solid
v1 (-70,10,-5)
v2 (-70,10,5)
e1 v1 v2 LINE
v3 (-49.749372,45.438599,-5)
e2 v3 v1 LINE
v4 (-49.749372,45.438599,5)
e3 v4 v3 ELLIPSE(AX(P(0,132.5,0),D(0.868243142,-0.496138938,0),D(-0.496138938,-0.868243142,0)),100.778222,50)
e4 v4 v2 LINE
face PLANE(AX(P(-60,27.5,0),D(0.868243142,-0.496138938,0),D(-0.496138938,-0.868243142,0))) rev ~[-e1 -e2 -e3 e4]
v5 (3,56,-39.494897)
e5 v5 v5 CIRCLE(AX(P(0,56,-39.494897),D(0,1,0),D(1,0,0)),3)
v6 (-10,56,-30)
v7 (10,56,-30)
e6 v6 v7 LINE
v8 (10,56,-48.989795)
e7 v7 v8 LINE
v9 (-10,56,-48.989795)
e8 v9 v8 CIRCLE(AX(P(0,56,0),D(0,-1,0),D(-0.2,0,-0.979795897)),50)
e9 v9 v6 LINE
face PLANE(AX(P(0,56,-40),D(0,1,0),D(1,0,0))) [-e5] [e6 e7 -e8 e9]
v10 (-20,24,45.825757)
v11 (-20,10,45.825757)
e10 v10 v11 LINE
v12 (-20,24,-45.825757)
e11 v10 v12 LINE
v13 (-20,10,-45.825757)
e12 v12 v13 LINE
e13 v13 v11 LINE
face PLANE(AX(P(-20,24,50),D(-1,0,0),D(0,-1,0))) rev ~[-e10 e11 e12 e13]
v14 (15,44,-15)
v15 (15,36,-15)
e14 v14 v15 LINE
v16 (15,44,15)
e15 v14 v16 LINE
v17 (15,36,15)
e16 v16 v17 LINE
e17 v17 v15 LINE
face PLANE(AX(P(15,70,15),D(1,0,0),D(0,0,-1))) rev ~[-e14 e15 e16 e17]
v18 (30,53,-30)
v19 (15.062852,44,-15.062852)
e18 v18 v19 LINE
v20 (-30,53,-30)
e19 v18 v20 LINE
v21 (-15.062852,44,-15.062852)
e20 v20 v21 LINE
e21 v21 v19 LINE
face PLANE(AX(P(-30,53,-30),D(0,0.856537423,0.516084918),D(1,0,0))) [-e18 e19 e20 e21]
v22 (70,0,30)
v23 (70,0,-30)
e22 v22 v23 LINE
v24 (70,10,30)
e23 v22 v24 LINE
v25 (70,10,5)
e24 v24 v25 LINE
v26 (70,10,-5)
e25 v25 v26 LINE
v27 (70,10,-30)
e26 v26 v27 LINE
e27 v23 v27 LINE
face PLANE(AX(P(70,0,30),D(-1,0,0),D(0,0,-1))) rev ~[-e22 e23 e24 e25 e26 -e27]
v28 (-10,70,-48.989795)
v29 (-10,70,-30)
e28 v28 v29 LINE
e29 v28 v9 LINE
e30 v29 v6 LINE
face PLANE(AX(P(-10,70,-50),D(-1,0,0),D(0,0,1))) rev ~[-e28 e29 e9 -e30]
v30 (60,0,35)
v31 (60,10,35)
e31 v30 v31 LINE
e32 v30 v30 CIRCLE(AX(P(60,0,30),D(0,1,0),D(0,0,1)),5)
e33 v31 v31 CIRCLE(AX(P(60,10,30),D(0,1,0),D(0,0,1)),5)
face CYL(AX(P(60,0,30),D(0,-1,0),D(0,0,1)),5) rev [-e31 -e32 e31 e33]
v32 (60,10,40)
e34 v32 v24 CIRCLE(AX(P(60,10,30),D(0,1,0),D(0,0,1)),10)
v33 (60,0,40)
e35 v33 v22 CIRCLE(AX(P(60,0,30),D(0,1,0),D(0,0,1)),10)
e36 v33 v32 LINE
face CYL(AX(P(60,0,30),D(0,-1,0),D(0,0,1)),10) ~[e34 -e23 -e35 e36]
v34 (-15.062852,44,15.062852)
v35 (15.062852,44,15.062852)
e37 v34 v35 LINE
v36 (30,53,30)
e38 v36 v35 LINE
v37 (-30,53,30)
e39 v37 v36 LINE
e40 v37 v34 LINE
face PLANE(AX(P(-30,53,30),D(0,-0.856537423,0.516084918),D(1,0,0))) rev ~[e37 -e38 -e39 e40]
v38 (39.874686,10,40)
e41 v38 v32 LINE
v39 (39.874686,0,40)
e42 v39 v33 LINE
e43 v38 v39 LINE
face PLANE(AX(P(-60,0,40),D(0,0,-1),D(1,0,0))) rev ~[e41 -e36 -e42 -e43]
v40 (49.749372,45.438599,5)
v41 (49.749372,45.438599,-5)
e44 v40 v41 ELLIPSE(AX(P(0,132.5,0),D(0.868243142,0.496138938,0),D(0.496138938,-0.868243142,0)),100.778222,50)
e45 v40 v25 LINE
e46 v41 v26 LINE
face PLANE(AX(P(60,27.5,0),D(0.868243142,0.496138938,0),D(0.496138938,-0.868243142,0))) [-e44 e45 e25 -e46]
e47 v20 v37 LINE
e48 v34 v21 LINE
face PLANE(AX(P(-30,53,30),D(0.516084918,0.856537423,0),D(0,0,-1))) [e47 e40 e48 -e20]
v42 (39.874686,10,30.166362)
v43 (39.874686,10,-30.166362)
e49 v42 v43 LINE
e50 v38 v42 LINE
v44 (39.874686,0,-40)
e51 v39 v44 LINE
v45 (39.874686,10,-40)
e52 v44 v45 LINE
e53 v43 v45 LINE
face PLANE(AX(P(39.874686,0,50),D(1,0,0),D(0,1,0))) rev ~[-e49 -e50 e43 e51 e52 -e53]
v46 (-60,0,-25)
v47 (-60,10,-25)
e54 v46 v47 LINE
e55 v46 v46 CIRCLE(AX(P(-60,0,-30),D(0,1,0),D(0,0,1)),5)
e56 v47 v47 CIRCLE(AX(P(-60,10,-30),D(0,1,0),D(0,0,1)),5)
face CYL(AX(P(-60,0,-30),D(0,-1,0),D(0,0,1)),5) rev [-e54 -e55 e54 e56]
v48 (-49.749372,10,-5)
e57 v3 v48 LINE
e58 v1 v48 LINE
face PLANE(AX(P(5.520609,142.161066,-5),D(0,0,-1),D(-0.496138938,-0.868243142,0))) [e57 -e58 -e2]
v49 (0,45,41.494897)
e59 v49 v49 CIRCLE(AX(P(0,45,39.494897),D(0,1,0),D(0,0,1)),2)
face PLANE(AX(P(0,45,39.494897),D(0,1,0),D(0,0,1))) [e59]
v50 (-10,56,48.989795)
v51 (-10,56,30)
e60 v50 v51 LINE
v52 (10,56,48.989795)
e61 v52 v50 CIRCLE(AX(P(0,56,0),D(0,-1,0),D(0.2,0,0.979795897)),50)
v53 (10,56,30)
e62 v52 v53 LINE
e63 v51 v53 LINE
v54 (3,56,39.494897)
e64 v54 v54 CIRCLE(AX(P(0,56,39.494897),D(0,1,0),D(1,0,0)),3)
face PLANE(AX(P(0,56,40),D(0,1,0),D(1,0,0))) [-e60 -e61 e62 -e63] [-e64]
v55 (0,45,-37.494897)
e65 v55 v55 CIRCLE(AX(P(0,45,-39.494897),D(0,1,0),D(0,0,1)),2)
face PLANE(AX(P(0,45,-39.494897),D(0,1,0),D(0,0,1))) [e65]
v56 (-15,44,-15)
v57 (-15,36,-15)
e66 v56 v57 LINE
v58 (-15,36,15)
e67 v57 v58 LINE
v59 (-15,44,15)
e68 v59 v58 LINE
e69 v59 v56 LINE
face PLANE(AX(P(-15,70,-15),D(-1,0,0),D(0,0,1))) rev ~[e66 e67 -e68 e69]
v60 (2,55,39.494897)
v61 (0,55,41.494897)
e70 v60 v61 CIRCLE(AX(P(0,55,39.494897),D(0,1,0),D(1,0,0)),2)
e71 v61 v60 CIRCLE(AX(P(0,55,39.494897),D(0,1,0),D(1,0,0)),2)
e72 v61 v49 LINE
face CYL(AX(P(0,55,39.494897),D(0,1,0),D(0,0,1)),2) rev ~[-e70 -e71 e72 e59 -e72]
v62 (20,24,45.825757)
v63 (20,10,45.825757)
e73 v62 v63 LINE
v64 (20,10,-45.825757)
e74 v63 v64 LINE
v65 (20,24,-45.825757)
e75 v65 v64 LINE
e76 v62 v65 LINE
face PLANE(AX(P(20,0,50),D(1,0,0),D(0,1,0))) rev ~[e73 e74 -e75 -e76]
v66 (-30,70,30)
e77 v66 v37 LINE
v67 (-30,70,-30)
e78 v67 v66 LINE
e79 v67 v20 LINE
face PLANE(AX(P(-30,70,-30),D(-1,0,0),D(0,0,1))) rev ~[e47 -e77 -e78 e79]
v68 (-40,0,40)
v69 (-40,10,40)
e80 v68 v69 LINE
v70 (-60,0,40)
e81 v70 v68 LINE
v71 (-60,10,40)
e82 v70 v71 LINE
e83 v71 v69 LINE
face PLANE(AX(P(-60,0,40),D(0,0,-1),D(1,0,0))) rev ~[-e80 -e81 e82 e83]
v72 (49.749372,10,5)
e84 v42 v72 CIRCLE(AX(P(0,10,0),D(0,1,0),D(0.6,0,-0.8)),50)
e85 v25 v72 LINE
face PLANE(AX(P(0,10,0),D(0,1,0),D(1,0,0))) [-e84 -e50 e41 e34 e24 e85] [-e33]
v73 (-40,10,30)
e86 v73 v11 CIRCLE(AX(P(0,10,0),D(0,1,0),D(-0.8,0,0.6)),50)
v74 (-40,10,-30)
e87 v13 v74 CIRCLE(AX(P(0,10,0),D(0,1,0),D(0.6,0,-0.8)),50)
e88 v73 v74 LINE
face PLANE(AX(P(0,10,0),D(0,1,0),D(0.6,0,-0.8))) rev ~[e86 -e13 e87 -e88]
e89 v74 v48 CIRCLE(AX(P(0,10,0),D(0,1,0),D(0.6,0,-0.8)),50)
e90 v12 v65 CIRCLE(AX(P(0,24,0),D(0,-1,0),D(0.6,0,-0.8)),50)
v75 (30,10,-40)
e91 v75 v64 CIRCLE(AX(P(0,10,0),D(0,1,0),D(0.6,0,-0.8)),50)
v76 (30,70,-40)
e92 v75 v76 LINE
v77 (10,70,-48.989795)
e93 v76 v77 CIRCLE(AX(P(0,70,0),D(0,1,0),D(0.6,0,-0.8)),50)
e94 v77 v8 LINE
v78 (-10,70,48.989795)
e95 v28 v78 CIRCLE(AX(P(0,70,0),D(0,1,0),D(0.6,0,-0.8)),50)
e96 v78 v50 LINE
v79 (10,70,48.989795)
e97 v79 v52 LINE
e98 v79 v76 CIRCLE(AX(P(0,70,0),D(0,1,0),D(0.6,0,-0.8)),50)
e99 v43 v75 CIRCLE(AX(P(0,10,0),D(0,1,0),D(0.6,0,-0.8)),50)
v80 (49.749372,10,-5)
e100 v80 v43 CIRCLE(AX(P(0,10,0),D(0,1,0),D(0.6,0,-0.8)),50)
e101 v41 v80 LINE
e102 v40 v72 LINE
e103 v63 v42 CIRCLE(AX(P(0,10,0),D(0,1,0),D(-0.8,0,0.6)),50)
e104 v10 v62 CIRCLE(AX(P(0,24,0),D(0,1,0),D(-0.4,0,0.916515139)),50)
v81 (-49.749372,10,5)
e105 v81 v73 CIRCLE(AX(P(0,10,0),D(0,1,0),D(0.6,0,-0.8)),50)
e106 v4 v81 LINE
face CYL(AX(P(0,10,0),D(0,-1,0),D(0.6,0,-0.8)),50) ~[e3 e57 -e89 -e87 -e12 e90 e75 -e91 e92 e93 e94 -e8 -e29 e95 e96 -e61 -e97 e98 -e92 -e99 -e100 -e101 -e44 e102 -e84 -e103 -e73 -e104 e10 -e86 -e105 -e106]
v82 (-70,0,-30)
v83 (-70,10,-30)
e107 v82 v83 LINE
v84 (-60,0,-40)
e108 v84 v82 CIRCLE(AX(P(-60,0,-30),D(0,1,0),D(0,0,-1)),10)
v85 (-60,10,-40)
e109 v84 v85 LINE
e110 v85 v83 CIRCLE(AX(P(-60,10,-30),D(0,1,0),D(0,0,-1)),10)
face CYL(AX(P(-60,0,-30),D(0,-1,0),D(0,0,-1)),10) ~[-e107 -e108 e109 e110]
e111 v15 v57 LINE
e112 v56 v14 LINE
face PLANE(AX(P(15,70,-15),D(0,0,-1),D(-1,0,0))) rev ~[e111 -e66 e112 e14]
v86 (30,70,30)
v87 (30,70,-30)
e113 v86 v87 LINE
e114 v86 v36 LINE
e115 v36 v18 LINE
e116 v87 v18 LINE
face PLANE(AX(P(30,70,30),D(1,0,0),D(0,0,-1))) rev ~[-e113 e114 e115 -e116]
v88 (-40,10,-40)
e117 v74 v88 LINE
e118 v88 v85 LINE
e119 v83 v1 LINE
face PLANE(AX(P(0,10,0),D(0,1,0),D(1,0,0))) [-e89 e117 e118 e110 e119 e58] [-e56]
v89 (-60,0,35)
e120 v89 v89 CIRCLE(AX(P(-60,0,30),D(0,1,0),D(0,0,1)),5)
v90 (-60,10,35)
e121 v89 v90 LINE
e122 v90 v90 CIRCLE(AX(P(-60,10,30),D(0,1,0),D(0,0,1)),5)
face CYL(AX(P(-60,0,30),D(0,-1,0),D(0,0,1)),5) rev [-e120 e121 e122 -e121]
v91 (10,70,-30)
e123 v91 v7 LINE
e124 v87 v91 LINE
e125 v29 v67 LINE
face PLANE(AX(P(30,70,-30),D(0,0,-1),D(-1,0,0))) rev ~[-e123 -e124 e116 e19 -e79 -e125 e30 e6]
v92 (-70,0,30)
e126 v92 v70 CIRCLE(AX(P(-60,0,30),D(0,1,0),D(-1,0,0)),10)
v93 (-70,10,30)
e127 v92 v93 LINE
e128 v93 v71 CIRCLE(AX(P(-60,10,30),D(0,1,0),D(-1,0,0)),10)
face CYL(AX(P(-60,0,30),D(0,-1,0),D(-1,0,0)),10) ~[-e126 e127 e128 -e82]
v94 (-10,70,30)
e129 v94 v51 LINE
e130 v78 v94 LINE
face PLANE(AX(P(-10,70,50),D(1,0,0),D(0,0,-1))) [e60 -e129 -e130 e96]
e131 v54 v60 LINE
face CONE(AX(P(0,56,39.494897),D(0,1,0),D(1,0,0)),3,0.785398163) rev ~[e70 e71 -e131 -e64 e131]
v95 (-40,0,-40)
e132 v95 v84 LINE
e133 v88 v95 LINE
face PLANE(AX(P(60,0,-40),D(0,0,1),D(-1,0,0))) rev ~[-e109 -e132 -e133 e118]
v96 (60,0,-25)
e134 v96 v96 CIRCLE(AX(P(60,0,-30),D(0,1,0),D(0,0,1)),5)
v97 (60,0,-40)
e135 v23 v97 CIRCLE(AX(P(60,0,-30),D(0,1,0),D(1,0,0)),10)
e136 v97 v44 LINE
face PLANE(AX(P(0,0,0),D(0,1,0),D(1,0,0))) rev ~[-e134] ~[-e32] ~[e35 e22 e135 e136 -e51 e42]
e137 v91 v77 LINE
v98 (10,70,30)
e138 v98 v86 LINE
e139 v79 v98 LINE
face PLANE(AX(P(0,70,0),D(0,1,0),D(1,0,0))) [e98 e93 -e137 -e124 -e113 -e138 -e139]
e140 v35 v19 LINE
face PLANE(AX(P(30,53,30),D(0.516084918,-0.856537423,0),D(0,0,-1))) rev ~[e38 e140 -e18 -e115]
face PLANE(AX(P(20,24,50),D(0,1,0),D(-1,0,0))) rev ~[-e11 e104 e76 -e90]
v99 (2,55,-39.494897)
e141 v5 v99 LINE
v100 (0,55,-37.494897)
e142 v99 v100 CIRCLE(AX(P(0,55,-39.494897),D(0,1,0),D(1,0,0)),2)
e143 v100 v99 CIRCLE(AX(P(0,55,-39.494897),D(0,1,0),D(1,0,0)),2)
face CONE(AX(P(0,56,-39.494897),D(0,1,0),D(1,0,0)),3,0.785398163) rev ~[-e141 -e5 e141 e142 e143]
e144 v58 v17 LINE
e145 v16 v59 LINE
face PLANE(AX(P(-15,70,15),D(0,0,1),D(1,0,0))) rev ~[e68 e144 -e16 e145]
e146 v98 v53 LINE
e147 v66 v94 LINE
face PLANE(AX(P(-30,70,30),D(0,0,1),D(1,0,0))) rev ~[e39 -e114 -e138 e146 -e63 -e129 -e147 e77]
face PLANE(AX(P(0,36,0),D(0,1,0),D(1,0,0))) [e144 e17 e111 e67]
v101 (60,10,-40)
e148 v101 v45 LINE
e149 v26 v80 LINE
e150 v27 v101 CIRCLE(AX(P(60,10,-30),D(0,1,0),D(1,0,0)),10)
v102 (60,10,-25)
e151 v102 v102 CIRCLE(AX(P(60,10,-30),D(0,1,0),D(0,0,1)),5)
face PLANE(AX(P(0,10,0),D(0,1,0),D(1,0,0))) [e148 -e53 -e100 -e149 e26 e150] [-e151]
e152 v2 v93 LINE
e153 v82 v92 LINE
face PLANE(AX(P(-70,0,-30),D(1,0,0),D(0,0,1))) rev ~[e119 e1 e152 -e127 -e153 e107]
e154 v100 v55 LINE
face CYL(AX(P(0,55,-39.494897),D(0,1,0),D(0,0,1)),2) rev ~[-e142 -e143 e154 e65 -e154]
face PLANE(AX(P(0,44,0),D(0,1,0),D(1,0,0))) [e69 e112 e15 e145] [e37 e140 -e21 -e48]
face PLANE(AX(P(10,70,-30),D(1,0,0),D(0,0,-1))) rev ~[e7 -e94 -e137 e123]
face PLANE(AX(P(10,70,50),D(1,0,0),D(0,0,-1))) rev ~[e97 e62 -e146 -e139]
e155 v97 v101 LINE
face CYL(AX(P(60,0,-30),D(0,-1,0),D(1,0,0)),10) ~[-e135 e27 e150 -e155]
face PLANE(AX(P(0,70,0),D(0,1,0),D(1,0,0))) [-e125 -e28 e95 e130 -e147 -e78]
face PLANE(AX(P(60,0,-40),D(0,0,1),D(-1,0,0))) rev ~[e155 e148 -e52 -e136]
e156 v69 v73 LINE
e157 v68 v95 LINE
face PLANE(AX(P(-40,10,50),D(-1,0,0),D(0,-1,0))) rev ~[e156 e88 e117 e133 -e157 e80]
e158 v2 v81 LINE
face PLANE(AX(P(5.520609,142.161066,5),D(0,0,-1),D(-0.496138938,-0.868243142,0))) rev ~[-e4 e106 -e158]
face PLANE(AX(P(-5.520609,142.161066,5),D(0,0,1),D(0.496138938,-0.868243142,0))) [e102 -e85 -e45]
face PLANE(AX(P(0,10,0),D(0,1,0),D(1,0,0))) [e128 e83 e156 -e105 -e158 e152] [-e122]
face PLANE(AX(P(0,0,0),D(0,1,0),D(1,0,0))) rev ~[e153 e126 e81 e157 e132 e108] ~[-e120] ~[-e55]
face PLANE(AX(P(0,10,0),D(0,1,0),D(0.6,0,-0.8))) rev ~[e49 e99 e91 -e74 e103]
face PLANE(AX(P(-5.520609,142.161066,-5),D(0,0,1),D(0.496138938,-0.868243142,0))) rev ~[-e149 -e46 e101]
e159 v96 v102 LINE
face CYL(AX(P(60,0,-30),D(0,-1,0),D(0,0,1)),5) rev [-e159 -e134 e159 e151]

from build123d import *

# Parameters (mm, degrees)
BASE_PLATE_SKETCH_R              = 5
BASE_PLATE_DEPTH                 = 10
BODY_CYLINDER_SKETCH_R           = 50
CYLINDRICAL_BODY_100_DEPTH       = 60
SQUARE_POCKET_60X60_DEPTH        = 17
LOWER_POCKET_DEPTH               = 17
DRAFTED_BOSS_SKETCH_W            = 30
DRAFTED_BOSS_SKETCH_H            = 30
DRAFTED_BOSS_DEPTH               = 9
DRAFTED_BOSS_DRAFT               = -58.93
SLOT_A_DEPTH                     = 34
INNER_BOSS_SKETCH_W              = 60
INNER_BOSS_SKETCH_H              = 60
INNER_BOSS_DEPTH                 = 44
SLOT_B_DEPTH                     = 34
CHANNEL_CUT_DEPTH                = 17
DRAFTED_CHANNEL_SKETCH_W         = 60
DRAFTED_CHANNEL_SKETCH_H         = 60
DRAFTED_CHANNEL_CUT_DEPTH        = 9
DRAFTED_CHANNEL_CUT_DRAFT        = -58.93
STEP_POCKET_SKETCH_W             = 20
STEP_POCKET_SKETCH_H             = 20
STEP_POCKET_DEPTH                = 14
PAD_HOLE_CHAMFER_SKETCH_R        = 3
PAD_HOLE_CHAMFER_DEPTH           = 1
PAD_HOLE_CHAMFER_DRAFT           = -45
PAD_HOLE_CHAMFER_PROFILE_2_DEPTH = 1
PAD_HOLE_CHAMFER_PROFILE_2_DRAFT = -45
PAD_HOLE_SKETCH_R                = 2
PAD_HOLE_DEPTH                   = 10
LEFT_SUPPORT_RIB_REACH           = 112.905
LEFT_RIB_SKETCH_WALL_W           = 264.12201887
LEFT_RIB_SKETCH_WALL_H           = 10
RIGHT_SUPPORT_RIB_REACH          = 112.905
RIGHT_RIB_SKETCH_WALL_W          = 264.12201887
RIGHT_RIB_SKETCH_WALL_H          = 10
SIDE_CUT_A_DEPTH                 = 126
SIDE_CUT_B_DEPTH                 = 202


with BuildPart() as part:
    # Base Plate Sketch → Base Plate (new body)
    with BuildSketch(Plane(origin=(0, 0, 0), x_dir=(1, 0, 0), z_dir=(0, 1, 0))):
        with BuildLine():
            Line((-60, -40), (0, -40))
            Line((0, -40), (60, -40))
            ThreePointArc((60, -40), (67.071067812, -37.071067812), (70, -30))
            Line((70, -30), (70, 0))
            Line((70, 0), (70, 30))
            ThreePointArc((70, 30), (67.071067812, 37.071067812), (60, 40))
            Line((60, 40), (-60, 40))
            ThreePointArc((-60, 40), (-67.071067812, 37.071067812), (-70, 30))
            Line((-70, 30), (-70, -30))
            ThreePointArc((-70, -30), (-67.071067812, -37.071067812), (-60, -40))
        make_face()
        with Locations(Location((-60, -30, 0), (0, 0, 270))):
            Circle(BASE_PLATE_SKETCH_R, mode=Mode.SUBTRACT)
        with Locations(Location((60, -30, 0), (0, 0, 270))):
            Circle(BASE_PLATE_SKETCH_R, mode=Mode.SUBTRACT)
        with Locations(Location((-60, 30, 0), (0, 0, 270))):
            Circle(BASE_PLATE_SKETCH_R, mode=Mode.SUBTRACT)
        with Locations(Location((60, 30, 0), (0, 0, 270))):
            Circle(BASE_PLATE_SKETCH_R, mode=Mode.SUBTRACT)
    extrude(amount=BASE_PLATE_DEPTH)

    # Body Cylinder Sketch → Cylindrical Body Ø100 (add)
    with BuildSketch(Plane(origin=(0, 10, 0), x_dir=(1, 0, 0), z_dir=(0, 1, 0))):
        with Locations(Location((0, 0, 0), (0, 0, 53.130102354))):
            Circle(BODY_CYLINDER_SKETCH_R)
    extrude(amount=CYLINDRICAL_BODY_100_DEPTH)

    # Square Pocket Sketch → Square Pocket 60x60 (cut)
    with BuildSketch(Plane(origin=(0, 70, 0), x_dir=(1, 0, 0), z_dir=(0, 1, 0))):
        Polygon((30, 0), (30, 30), (-30, 30), (-30, -30), (30, -30), align=None)
    extrude(amount=-SQUARE_POCKET_60X60_DEPTH, mode=Mode.SUBTRACT)

    # Lower Pocket Sketch → Lower Pocket (cut)
    with BuildSketch(Plane(origin=(0, 53, 0), x_dir=(1, 0, 0), z_dir=(0, 1, 0))):
        Polygon((15, 0), (15, 15), (-15, 15), (-15, -15), (15, -15), align=None)
    extrude(amount=-LOWER_POCKET_DEPTH, mode=Mode.SUBTRACT)


with BuildPart() as body_2:
    # Drafted Boss Sketch → Drafted Boss (with draft: the straight prism first)
    with BuildSketch(Plane(origin=(0, 53, 0), x_dir=(1, 0, 0), z_dir=(0, 1, 0))):
        Rectangle(DRAFTED_BOSS_SKETCH_W, DRAFTED_BOSS_SKETCH_H)
    extrude(amount=DRAFTED_BOSS_DEPTH)
    # Drafted Boss: the draft: its side faces are tilted about the plane it starts from
    drafted_boss_sides = [body_2.faces().sort_by_distance(p)[0] for p in [
        (-15, 57.5, 0),
        (0, 57.5, 15),
        (15, 57.5, 0),
        (0, 57.5, -15),
    ]]
    draft(drafted_boss_sides, Plane(origin=(0, 53, 0), x_dir=(1, 0, 0), z_dir=(0, 1, 0)), DRAFTED_BOSS_DRAFT)


with BuildPart() as slot_a_tool:
    # Slot A Sketch → Slot A (new body)
    with BuildSketch(Plane(origin=(0, 62, 0), x_dir=(1, 0, 0), z_dir=(0, 1, 0))):
        Polygon((15, 0), (15, 15), (-15, 15), (-15, -15), (15, -15), align=None)
    extrude(amount=-SLOT_A_DEPTH)


with BuildPart() as part_1:
    add(part.part)

    # Slot A: cut by slot_a_tool
    add(slot_a_tool.part, mode=Mode.SUBTRACT)



with BuildPart() as body_2_1:
    add(body_2.part)

    # Slot A: cut by slot_a_tool
    add(slot_a_tool.part, mode=Mode.SUBTRACT)


with BuildPart() as part_2:
    add(part_1.part)

    add(body_2_1.part)  # Inner Boss merges body 2
    # Inner Boss Sketch → Inner Boss (add)
    with BuildSketch(Plane(origin=(0, 70, 0), x_dir=(1, 0, 0), z_dir=(0, 1, 0))):
        Rectangle(INNER_BOSS_SKETCH_W, INNER_BOSS_SKETCH_H)
    extrude(amount=-INNER_BOSS_DEPTH)

    # Slot B Sketch → Slot B (cut)
    with BuildSketch(Plane(origin=(0, 70, 0), x_dir=(1, 0, 0), z_dir=(0, 1, 0))):
        Polygon((15, 0), (15, 15), (-15, 15), (-15, -15), (15, -15), align=None)
    extrude(amount=-SLOT_B_DEPTH, mode=Mode.SUBTRACT)

    # Channel Sketch → Channel Cut (cut)
    with BuildSketch(Plane(origin=(0, 70, 0), x_dir=(1, 0, 0), z_dir=(0, 1, 0))):
        Polygon((30, 0), (30, 30), (-30, 30), (-30, -30), (30, -30), align=None)
    extrude(amount=-CHANNEL_CUT_DEPTH, mode=Mode.SUBTRACT)


with BuildPart() as drafted_channel_cut_tool:
    # Drafted Channel Sketch → Drafted Channel Cut (with draft: the straight prism first)
    with BuildSketch(Plane(origin=(0, 53, 0), x_dir=(1, 0, 0), z_dir=(0, 1, 0))):
        Rectangle(DRAFTED_CHANNEL_SKETCH_W, DRAFTED_CHANNEL_SKETCH_H)
    extrude(amount=-DRAFTED_CHANNEL_CUT_DEPTH)
    # Drafted Channel Cut: the draft: its side faces are tilted about the plane it starts from
    drafted_channel_cut_sides = [drafted_channel_cut_tool.faces().sort_by_distance(p)[0] for p in [
        (-30, 48.5, 0),
        (0, 48.5, 30),
        (30, 48.5, 0),
        (0, 48.5, -30),
    ]]
    draft(drafted_channel_cut_sides, Plane(origin=(0, 53, 0), x_dir=(1, 0, 0), z_dir=(0, 1, 0)), DRAFTED_CHANNEL_CUT_DRAFT)


with BuildPart() as part_3:
    add(part_2.part)

    # Drafted Channel Cut: cut by drafted_channel_cut_tool
    add(drafted_channel_cut_tool.part, mode=Mode.SUBTRACT)

    # Step Pocket Sketch → Step Pocket (cut)
    with BuildSketch(Plane(origin=(0, 70, 0), x_dir=(1, 0, 0), z_dir=(0, 1, 0))):
        with Locations((0, -40)):
            Rectangle(STEP_POCKET_SKETCH_W, STEP_POCKET_SKETCH_H)
        Polygon((0, 30), (10, 30), (10, 50), (-10, 50), (-10, 30), align=None)
    extrude(amount=-STEP_POCKET_DEPTH, mode=Mode.SUBTRACT)


with BuildPart() as pad_hole_chamfer_tool:
    # Pad Hole Chamfer Sketch → Pad Hole Chamfer (with draft: the straight prism first)
    with BuildSketch(Plane(origin=(0, 56, 0), x_dir=(1, 0, 0), z_dir=(0, 1, 0))):
        with Locations((0, -39.494897428)):
            Circle(PAD_HOLE_CHAMFER_SKETCH_R)
    extrude(amount=-PAD_HOLE_CHAMFER_DEPTH)
    # Pad Hole Chamfer: the draft: its side faces are tilted about the plane it starts from
    pad_hole_chamfer_sides = [pad_hole_chamfer_tool.faces().sort_by_distance(p)[0] for p in [
        (-3, 55.5, 39.494897428),
    ]]
    draft(pad_hole_chamfer_sides, Plane(origin=(0, 56, 0), x_dir=(1, 0, 0), z_dir=(0, 1, 0)), PAD_HOLE_CHAMFER_DRAFT)


with BuildPart() as part_4:
    add(part_3.part)

    # Pad Hole Chamfer: cut by pad_hole_chamfer_tool
    add(pad_hole_chamfer_tool.part, mode=Mode.SUBTRACT)


with BuildPart() as pad_hole_chamfer_profile_2_tool:
    # Pad Hole Chamfer Sketch → Pad Hole Chamfer profile 2 (with draft: the straight prism first)
    with BuildSketch(Plane(origin=(0, 56, 0), x_dir=(1, 0, 0), z_dir=(0, 1, 0))):
        with Locations((0, 39.494897428)):
            Circle(PAD_HOLE_CHAMFER_SKETCH_R)
    extrude(amount=-PAD_HOLE_CHAMFER_PROFILE_2_DEPTH)
    # Pad Hole Chamfer profile 2: the draft: its side faces are tilted about the plane it starts from
    pad_hole_chamfer_profile_2_sides = [pad_hole_chamfer_profile_2_tool.faces().sort_by_distance(p)[0] for p in [
        (-3, 55.5, -39.494897428),
    ]]
    draft(pad_hole_chamfer_profile_2_sides, Plane(origin=(0, 56, 0), x_dir=(1, 0, 0), z_dir=(0, 1, 0)), PAD_HOLE_CHAMFER_PROFILE_2_DRAFT)


with BuildPart() as part_5:
    add(part_4.part)

    # Pad Hole Chamfer profile 2: cut by pad_hole_chamfer_profile_2_tool
    add(pad_hole_chamfer_profile_2_tool.part, mode=Mode.SUBTRACT)

    # Pad Hole Sketch → Pad Hole (cut)
    with BuildSketch(Plane(origin=(0, 55, 0), x_dir=(1, 0, 0), z_dir=(0, 1, 0))):
        with Locations(Location((0, 39.494897428, 0), (0, 0, 270))):
            Circle(PAD_HOLE_SKETCH_R)
        with Locations(Location((0, -39.494897428, 0), (0, 0, 270))):
            Circle(PAD_HOLE_SKETCH_R)
    extrude(amount=-PAD_HOLE_DEPTH, mode=Mode.SUBTRACT)

    # Left Rib Sketch wall → Left Support Rib (add, up to next)
    with BuildSketch(Plane(origin=(-60, 27.5, 0), x_dir=(-0.496138938357, -0.868243142124, 0), z_dir=(0.868243142124, -0.496138938357, 0)), mode=Mode.PRIVATE) as left_support_rib_sk1:
        Rectangle(LEFT_RIB_SKETCH_WALL_W, LEFT_RIB_SKETCH_WALL_H)
    left_support_rib_tool1 = extrude(left_support_rib_sk1.sketch, amount=LEFT_SUPPORT_RIB_REACH, mode=Mode.PRIVATE) - part_5.part
    add(left_support_rib_tool1.solids().sort_by_distance((-60, 27.5, 0))[0])

    # Right Rib Sketch wall → Right Support Rib (add, up to next)
    with BuildSketch(Plane(origin=(60, 27.5, 0), x_dir=(0.496138938357, -0.868243142124, 0), z_dir=(0.868243142124, 0.496138938357, 0)), mode=Mode.PRIVATE) as right_support_rib_sk1:
        Rectangle(RIGHT_RIB_SKETCH_WALL_W, RIGHT_RIB_SKETCH_WALL_H)
    right_support_rib_tool1 = extrude(right_support_rib_sk1.sketch, amount=-RIGHT_SUPPORT_RIB_REACH, mode=Mode.PRIVATE) - part_5.part
    add(right_support_rib_tool1.solids().sort_by_distance((60, 27.5, 0))[0])

    # Side Cut A Sketch → Side Cut A (cut)
    with BuildSketch(Plane.XY.offset(50)):
        Polygon((0, 10), (-40, 10), (-40, 0), (39.874685928, 0), (39.874685928, 10), align=None)
    extrude(amount=-SIDE_CUT_A_DEPTH, mode=Mode.SUBTRACT)

    # Side Cut B Sketch → Side Cut B (cut)
    with BuildSketch(Plane.XY.offset(50)):
        Polygon((0, 0), (20, 0), (20, 24), (-20, 24), (-20, 0), align=None)
    extrude(amount=-SIDE_CUT_B_DEPTH, mode=Mode.SUBTRACT)


solid = part_5.part
